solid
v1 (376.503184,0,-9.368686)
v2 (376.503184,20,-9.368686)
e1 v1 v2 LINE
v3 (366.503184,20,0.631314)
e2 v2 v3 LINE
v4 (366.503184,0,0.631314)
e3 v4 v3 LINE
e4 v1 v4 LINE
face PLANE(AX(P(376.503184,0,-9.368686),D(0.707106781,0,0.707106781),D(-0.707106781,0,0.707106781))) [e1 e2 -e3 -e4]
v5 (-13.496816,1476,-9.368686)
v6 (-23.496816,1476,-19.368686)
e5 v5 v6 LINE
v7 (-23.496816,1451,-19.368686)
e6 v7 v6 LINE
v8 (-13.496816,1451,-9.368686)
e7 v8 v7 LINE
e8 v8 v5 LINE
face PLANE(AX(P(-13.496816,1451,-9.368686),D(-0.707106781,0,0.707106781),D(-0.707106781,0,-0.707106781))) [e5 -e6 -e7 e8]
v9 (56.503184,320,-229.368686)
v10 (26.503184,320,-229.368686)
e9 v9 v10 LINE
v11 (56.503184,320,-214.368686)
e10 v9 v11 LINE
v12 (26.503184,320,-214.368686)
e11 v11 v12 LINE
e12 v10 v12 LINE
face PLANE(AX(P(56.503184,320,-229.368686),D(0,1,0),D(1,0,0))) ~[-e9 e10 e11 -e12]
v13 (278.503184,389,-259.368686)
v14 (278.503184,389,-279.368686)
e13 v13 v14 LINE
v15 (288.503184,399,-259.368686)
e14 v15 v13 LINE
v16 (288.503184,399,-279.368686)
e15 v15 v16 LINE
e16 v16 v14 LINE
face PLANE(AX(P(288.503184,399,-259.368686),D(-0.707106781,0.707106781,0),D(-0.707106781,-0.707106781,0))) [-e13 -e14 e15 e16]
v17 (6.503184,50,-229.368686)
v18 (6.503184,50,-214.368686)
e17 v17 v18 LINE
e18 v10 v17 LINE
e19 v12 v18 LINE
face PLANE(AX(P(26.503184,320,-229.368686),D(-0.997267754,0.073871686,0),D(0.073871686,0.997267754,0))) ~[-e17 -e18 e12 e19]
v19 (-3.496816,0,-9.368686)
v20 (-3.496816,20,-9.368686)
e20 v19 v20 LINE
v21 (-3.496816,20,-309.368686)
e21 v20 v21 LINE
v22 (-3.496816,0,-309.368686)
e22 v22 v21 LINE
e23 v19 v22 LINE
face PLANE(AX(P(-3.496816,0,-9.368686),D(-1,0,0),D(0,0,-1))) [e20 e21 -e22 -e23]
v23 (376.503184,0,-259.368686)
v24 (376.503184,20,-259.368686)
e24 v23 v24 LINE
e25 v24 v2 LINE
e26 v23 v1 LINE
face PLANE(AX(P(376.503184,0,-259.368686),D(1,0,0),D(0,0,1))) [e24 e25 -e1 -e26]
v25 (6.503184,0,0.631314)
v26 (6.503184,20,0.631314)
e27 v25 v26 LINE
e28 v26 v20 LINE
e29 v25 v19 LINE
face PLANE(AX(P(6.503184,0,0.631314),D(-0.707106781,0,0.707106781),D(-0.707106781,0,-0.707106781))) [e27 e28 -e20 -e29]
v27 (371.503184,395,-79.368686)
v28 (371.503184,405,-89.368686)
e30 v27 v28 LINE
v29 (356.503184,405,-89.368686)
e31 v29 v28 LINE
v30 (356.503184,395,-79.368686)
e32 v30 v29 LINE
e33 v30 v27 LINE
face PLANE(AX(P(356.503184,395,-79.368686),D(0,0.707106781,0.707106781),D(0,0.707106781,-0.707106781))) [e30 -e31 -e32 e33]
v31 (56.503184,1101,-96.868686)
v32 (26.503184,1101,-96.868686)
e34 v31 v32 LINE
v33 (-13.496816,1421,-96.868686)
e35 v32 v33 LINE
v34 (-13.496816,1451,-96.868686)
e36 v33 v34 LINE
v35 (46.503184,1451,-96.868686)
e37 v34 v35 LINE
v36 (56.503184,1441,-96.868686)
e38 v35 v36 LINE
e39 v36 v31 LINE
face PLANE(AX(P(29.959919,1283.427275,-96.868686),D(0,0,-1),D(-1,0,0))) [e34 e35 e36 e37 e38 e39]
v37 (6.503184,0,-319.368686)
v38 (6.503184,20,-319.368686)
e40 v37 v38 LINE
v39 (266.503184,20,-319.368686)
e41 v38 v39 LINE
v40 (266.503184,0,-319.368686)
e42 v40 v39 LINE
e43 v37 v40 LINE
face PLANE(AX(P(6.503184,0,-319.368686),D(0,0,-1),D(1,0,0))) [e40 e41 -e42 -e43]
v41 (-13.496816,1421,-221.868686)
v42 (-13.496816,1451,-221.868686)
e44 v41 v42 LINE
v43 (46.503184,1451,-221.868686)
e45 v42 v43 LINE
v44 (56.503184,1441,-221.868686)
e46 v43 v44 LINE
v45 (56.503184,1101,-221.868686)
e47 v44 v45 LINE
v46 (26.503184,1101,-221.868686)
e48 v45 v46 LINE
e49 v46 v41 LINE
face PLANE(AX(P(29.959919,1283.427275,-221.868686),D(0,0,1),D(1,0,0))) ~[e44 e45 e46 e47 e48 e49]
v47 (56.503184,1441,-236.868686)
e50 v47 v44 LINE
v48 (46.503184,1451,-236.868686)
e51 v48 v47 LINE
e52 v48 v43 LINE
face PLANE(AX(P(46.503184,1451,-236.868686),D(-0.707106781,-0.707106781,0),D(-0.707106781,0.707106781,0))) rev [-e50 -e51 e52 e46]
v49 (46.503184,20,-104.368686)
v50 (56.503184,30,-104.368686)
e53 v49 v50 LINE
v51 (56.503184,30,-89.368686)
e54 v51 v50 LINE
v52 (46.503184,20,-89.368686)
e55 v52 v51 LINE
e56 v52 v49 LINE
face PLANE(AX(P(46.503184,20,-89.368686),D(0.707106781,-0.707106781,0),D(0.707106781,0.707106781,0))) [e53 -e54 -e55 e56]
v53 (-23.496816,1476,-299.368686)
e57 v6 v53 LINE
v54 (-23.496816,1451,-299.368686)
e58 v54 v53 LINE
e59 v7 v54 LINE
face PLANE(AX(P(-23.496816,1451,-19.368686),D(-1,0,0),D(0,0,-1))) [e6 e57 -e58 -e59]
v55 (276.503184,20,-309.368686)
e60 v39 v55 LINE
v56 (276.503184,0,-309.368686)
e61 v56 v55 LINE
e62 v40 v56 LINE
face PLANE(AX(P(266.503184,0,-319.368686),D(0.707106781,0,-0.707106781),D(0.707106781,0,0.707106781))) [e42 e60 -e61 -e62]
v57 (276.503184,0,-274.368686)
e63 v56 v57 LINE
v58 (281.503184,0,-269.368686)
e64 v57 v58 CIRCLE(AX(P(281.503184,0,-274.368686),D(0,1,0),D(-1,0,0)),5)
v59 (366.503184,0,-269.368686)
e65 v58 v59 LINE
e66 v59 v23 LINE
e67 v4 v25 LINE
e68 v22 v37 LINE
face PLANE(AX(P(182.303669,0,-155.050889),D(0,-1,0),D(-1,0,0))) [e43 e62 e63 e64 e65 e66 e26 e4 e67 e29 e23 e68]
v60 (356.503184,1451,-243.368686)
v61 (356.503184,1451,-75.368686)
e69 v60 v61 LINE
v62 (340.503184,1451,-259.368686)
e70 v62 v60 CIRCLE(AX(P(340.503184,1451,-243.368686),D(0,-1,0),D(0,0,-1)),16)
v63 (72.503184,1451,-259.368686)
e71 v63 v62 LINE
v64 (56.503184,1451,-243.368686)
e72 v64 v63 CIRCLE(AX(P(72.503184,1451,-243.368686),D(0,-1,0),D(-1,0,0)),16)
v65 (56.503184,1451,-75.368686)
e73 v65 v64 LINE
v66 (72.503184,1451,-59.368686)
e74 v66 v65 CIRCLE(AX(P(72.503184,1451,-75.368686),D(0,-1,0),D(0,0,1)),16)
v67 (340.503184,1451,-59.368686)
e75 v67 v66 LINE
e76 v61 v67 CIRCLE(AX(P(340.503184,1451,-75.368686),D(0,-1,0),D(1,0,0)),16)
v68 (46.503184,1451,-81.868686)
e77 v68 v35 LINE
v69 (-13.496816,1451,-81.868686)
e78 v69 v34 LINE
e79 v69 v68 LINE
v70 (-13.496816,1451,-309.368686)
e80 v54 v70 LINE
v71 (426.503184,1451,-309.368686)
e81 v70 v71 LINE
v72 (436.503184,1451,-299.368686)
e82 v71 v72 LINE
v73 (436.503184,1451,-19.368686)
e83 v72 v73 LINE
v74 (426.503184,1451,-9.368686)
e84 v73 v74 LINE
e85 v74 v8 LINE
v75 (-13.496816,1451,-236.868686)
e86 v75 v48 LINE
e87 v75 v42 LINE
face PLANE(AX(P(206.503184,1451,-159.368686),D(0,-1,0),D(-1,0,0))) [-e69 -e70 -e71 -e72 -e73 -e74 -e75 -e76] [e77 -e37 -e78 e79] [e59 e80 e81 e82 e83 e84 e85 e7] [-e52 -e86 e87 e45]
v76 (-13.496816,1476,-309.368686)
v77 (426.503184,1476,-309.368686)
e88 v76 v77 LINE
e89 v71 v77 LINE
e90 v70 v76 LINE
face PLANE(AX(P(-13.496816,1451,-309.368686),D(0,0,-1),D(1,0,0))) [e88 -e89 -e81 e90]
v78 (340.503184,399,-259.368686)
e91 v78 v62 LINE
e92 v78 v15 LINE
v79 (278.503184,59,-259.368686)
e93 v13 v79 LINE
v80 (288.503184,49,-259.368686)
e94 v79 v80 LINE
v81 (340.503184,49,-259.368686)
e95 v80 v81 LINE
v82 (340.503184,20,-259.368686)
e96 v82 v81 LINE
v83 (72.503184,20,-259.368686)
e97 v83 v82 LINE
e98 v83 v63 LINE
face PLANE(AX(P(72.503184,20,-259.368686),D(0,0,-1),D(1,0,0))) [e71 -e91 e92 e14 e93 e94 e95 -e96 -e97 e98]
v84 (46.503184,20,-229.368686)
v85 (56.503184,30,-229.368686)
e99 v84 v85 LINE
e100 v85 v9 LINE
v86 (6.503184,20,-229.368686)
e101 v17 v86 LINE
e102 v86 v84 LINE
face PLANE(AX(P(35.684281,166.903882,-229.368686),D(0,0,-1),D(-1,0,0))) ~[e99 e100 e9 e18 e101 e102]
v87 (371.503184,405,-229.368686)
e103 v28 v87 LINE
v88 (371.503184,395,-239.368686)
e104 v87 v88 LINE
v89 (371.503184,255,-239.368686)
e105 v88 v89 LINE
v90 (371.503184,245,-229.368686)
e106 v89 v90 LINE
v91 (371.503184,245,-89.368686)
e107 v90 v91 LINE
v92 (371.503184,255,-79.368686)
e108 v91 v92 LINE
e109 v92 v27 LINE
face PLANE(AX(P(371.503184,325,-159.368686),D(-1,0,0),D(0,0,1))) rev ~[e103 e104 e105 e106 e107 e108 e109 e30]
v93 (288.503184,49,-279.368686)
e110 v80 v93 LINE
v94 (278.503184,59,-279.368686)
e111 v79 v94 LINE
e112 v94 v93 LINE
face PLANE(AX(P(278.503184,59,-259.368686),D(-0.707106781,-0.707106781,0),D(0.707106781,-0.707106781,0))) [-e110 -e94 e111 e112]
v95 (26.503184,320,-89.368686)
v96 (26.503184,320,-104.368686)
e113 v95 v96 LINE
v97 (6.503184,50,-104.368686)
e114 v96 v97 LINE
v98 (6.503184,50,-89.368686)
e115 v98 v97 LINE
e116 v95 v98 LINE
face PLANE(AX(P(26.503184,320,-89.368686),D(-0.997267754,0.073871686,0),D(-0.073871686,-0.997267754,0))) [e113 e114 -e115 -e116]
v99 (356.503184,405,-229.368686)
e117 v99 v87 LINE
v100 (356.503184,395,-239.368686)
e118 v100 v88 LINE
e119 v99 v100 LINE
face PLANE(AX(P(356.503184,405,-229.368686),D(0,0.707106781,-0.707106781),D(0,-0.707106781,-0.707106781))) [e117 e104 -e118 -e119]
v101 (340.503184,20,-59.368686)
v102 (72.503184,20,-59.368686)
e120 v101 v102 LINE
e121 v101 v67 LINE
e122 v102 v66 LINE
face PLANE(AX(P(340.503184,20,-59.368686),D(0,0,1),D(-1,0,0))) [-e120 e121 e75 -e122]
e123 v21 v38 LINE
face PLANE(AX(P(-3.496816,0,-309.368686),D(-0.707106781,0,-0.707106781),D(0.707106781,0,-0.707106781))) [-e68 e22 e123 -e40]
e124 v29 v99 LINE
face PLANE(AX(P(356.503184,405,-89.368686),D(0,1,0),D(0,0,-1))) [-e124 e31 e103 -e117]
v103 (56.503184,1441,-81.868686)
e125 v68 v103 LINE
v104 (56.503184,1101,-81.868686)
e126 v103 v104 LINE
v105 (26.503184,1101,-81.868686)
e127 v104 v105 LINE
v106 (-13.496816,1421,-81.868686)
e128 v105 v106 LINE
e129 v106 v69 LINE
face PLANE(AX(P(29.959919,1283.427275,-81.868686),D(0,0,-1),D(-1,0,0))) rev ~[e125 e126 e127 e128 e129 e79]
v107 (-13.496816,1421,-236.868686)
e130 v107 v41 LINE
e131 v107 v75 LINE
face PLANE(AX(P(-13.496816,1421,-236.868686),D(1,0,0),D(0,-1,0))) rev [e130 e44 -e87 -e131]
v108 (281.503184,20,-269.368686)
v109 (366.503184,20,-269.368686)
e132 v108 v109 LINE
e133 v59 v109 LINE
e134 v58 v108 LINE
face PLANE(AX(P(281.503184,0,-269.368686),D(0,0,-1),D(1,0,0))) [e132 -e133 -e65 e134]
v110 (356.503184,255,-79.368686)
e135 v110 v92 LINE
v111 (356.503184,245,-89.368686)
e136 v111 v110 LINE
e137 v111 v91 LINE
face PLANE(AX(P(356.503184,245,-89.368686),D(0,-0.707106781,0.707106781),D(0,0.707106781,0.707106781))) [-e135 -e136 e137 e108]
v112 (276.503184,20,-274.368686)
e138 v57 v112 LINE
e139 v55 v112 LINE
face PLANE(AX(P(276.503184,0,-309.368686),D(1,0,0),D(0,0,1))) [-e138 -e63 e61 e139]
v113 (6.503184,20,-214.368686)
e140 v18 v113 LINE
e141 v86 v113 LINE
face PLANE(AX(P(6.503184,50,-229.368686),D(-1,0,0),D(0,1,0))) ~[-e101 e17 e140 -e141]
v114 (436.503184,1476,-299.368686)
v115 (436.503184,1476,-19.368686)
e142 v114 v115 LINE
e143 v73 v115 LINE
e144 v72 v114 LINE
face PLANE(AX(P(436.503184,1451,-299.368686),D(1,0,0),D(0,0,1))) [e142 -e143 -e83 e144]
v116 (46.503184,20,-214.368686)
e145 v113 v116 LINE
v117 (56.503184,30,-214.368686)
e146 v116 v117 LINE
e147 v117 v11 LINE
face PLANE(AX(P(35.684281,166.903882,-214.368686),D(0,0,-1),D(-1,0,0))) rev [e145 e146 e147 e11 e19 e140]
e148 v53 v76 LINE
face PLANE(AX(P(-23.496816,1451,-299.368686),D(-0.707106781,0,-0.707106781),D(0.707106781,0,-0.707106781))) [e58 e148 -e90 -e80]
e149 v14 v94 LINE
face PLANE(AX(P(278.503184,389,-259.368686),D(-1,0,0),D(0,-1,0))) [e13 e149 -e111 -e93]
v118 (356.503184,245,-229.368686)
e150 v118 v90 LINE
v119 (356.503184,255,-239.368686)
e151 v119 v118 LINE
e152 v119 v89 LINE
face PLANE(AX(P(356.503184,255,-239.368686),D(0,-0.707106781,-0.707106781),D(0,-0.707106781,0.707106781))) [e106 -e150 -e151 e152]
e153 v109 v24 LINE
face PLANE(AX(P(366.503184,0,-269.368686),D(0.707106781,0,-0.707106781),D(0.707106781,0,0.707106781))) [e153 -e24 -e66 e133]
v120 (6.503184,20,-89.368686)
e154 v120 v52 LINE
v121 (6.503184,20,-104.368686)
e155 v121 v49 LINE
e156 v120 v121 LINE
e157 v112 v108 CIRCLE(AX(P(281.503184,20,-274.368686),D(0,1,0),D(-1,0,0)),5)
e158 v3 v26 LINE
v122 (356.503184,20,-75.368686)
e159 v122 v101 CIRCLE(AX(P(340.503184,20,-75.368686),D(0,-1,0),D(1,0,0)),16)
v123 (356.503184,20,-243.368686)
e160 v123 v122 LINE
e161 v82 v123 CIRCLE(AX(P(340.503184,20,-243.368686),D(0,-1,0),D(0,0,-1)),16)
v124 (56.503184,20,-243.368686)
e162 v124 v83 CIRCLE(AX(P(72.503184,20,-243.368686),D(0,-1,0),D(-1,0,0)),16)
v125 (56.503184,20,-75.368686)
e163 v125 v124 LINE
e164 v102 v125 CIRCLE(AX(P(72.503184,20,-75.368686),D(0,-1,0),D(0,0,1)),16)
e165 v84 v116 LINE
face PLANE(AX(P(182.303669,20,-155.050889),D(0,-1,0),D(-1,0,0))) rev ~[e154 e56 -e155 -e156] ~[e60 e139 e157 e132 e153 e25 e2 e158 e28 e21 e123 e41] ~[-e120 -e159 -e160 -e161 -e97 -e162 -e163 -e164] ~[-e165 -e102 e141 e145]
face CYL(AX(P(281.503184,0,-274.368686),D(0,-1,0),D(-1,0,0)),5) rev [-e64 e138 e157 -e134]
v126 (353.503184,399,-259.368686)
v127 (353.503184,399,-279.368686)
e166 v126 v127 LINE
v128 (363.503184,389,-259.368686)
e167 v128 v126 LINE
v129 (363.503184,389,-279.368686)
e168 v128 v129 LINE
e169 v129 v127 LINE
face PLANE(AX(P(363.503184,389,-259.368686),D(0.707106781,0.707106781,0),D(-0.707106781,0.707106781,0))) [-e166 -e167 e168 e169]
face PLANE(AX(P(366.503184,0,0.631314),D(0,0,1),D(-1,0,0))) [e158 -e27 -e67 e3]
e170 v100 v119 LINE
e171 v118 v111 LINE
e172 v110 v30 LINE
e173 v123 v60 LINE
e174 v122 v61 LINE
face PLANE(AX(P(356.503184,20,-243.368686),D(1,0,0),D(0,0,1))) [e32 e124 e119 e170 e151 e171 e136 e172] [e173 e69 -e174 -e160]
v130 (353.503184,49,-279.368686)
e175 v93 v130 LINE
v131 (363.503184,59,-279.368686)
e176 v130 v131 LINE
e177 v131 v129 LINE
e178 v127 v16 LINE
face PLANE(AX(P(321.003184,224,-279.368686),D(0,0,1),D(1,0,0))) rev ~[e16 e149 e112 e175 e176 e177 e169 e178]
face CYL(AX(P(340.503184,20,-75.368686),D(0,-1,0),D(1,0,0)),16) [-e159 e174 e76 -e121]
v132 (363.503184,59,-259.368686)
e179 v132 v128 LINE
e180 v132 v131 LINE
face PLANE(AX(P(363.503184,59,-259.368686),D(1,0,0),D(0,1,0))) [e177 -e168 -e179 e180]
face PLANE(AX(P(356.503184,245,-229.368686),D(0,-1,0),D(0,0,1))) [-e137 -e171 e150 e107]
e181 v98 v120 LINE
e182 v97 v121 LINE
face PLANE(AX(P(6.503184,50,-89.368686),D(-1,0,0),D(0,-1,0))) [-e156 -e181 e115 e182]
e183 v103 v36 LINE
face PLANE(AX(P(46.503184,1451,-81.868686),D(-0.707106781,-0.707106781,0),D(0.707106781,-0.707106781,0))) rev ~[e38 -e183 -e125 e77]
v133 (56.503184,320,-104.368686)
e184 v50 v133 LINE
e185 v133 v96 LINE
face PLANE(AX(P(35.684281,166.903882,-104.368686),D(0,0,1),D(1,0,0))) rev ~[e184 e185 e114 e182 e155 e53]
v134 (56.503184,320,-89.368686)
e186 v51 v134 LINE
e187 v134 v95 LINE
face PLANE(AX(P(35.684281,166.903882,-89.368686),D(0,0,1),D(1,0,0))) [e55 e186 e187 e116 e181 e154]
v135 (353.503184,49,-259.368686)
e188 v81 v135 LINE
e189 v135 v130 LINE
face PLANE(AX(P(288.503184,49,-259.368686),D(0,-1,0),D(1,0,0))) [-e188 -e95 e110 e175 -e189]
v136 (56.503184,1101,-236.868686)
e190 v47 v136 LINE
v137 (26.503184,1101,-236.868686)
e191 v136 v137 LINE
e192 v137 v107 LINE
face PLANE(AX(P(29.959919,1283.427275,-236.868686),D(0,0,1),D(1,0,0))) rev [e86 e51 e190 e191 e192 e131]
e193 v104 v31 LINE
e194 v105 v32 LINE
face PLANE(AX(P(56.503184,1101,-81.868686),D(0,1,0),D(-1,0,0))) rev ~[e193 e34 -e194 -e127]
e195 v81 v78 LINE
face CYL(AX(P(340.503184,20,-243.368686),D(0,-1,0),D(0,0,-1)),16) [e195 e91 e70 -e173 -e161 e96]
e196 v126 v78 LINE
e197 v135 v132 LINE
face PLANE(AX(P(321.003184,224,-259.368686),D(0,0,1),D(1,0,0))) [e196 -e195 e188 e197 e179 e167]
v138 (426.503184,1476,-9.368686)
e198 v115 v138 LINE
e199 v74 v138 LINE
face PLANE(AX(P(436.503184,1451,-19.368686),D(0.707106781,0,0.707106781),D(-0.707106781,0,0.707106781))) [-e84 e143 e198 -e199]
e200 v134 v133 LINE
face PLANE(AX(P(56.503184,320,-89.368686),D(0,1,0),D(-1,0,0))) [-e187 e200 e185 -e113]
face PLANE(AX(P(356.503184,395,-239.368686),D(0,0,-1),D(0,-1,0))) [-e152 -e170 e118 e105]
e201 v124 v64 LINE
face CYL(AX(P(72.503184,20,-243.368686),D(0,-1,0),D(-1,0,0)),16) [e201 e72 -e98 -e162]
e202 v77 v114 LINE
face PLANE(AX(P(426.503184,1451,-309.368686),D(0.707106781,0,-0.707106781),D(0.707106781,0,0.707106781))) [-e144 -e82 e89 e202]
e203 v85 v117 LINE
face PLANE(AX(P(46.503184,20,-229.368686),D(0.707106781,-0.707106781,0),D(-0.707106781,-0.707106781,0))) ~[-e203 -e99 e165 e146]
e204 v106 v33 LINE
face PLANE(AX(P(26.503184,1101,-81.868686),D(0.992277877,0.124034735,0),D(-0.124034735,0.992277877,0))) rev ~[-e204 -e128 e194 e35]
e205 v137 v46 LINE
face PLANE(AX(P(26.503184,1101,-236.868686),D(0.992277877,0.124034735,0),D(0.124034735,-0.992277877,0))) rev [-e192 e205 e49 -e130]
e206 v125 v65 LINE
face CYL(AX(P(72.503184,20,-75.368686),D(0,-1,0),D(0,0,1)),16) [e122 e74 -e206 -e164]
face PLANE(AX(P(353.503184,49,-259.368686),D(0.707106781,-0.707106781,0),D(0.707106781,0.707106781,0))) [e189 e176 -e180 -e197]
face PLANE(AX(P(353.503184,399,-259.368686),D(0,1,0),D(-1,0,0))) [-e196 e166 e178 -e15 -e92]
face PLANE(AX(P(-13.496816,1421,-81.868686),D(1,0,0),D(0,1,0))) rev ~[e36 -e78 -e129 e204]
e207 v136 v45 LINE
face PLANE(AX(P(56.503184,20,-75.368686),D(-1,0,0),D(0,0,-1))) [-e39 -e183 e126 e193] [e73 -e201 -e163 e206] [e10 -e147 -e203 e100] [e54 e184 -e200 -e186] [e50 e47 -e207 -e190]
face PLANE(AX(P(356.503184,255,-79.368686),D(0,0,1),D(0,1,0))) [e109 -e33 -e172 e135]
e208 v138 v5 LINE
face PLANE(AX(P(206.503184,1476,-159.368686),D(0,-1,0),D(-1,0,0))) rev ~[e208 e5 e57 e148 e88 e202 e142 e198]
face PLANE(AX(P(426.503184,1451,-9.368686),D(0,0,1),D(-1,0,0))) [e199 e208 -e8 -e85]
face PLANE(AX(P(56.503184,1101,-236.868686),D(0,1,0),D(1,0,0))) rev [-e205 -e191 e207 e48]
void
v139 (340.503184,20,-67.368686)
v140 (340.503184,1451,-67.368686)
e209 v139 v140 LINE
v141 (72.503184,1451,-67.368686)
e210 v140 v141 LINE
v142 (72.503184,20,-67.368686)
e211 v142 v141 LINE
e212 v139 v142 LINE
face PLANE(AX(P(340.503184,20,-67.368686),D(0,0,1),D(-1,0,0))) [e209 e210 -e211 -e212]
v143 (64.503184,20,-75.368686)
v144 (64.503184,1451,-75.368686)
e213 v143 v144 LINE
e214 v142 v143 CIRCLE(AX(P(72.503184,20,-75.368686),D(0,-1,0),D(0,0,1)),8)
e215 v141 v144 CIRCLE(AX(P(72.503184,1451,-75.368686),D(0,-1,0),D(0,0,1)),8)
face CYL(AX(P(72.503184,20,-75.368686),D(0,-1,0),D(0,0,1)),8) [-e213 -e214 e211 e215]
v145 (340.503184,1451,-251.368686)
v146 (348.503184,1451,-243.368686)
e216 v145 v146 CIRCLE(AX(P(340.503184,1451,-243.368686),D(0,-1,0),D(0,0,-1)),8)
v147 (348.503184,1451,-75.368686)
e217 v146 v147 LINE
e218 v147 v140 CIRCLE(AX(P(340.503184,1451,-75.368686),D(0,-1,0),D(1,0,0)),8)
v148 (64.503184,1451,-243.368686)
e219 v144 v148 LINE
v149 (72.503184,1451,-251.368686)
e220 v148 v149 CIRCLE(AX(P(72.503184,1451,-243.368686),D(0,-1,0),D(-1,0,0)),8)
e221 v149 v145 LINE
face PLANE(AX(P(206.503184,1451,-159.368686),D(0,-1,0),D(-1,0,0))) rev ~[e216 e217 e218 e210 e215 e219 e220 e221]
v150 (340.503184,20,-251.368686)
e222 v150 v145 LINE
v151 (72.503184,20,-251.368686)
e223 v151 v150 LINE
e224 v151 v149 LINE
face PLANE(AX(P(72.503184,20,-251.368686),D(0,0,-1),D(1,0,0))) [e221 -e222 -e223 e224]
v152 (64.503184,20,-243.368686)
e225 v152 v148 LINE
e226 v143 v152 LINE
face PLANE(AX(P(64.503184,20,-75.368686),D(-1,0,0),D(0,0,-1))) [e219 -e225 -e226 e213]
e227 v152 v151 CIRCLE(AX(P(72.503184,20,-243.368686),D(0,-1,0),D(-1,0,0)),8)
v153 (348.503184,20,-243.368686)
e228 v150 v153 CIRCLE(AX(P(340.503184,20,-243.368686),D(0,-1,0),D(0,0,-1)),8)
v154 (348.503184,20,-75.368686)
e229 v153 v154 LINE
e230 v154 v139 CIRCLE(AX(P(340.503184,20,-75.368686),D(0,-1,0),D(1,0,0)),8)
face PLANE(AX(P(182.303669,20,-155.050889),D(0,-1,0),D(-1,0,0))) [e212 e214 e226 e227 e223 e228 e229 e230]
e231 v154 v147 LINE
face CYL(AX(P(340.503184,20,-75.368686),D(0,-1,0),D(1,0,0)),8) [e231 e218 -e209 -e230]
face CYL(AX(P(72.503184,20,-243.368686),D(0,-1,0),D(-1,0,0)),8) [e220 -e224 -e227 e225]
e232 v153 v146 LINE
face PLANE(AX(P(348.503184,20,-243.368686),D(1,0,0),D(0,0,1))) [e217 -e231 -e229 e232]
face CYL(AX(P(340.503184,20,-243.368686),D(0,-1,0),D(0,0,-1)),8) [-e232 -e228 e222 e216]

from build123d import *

# Parameters (mm, degrees)
BOSS_EXTRUDE1_DEPTH  = 20
BOSS_EXTRUDE2_DEPTH  = 1431
BOSS_EXTRUDE3_DEPTH  = 25
BOSS_EXTRUDE4_START  = -22.5
BOSS_EXTRUDE4_DEPTH  = 15
BOSS_EXTRUDE5_DEPTH  = 15
BOSS_EXTRUDE9_START  = -30
BOSS_EXTRUDE9_DEPTH  = 15
BOSS_EXTRUDE10_DEPTH = 20


with BuildPart() as part:
    # Sketch1 → Boss-Extrude1 (new body)
    with BuildSketch(Plane(origin=(0, 0, 0), x_dir=(1, 0, 0), z_dir=(0, 1, 0))):
        with BuildLine():
            Line((-3.496816057, 9.368686005), (-3.496816057, 309.368686005))
            Line((-3.496816057, 309.368686005), (6.503183943, 319.368686005))
            Line((6.503183943, 319.368686005), (141.657748152, 319.368686005))
            Line((141.657748152, 319.368686005), (266.503183943, 319.368686005))
            Line((266.503183943, 319.368686005), (276.503183943, 309.368686005))
            Line((276.503183943, 309.368686005), (276.503183943, 274.368686005))
            ThreePointArc((276.503183943, 274.368686005), (277.967650037, 270.833152099), (281.503183943, 269.368686005))
            Line((281.503183943, 269.368686005), (366.503183943, 269.368686005))
            Line((366.503183943, 269.368686005), (376.503183943, 259.368686005))
            Line((376.503183943, 259.368686005), (376.503183943, 9.368686005))
            Line((376.503183943, 9.368686005), (366.503183943, -0.631313995))
            Line((366.503183943, -0.631313995), (6.503183943, -0.631313995))
            Line((6.503183943, -0.631313995), (-3.496816057, 9.368686005))
        make_face()
    extrude(amount=BOSS_EXTRUDE1_DEPTH)

    # Sketch2 → Boss-Extrude2 (add)
    with BuildSketch(Plane(origin=(0, 20, 0), x_dir=(1, 0, 0), z_dir=(0, 1, 0))):
        with BuildLine():
            Line((72.503183943, 259.368686005), (340.503183943, 259.368686005))
            ThreePointArc((340.503183943, 259.368686005), (351.816892442, 254.682394504), (356.503183943, 243.368686005))
            Line((356.503183943, 243.368686005), (356.503183943, 75.368686005))
            ThreePointArc((356.503183943, 75.368686005), (351.816892442, 64.054977506), (340.503183943, 59.368686005))
            Line((340.503183943, 59.368686005), (72.503183943, 59.368686005))
            ThreePointArc((72.503183943, 59.368686005), (61.189475444, 64.054977506), (56.503183943, 75.368686005))
            Line((56.503183943, 75.368686005), (56.503183943, 243.368686005))
            ThreePointArc((56.503183943, 243.368686005), (61.189475444, 254.682394504), (72.503183943, 259.368686005))
        make_face()
        with BuildLine():
            Line((72.503183943, 251.368686005), (340.503183943, 251.368686005))
            ThreePointArc((340.503183943, 251.368686005), (346.160038192, 249.025540255), (348.503183943, 243.368686005))
            Line((348.503183943, 243.368686005), (348.503183943, 75.368686005))
            ThreePointArc((348.503183943, 75.368686005), (346.160038192, 69.711831756), (340.503183943, 67.368686005))
            Line((340.503183943, 67.368686005), (72.503183943, 67.368686005))
            ThreePointArc((72.503183943, 67.368686005), (66.846329693, 69.711831756), (64.503183943, 75.368686005))
            Line((64.503183943, 75.368686005), (64.503183943, 243.368686005))
            ThreePointArc((64.503183943, 243.368686005), (66.846329693, 249.025540255), (72.503183943, 251.368686005))
        make_face(mode=Mode.SUBTRACT)
    extrude(amount=BOSS_EXTRUDE2_DEPTH)

    # Sketch3 → Boss-Extrude3 (add)
    with BuildSketch(Plane(origin=(0, 1451, 0), x_dir=(1, 0, 0), z_dir=(0, 1, 0))):
        Polygon((-13.496816057, 309.368686005), (426.503183943, 309.368686005), (436.503183943, 299.368686005), (436.503183943, 19.368686005), (426.503183943, 9.368686005), (-13.496816057, 9.368686005), (-23.496816057, 19.368686005), (-23.496816057, 299.368686005), align=None)
    extrude(amount=BOSS_EXTRUDE3_DEPTH)

    # Sketch4 → Boss-Extrude4 (add)
    with BuildSketch(Plane.XY.offset(-59.368686005).offset(BOSS_EXTRUDE4_START)):
        Polygon((-13.496816057, 1451), (46.503183943, 1451), (56.503183943, 1441), (56.503183943, 1101), (26.503183943, 1101), (-13.496816057, 1421), align=None)
    boss_extrude4 = extrude(amount=-BOSS_EXTRUDE4_DEPTH)

    # Mirror1: Boss-Extrude4 across plane
    add(boss_extrude4.mirror(Plane.XY.offset(-159.368686005)))

    # Sketch5 → Boss-Extrude5 (add)
    with BuildSketch(Plane(origin=(356.503183943, 0, 0), x_dir=(0, 0, -1), z_dir=(1, 0, 0))):
        Polygon((89.368686005, 405), (229.368686005, 405), (239.368686005, 395), (239.368686005, 255), (229.368686005, 245), (89.368686005, 245), (79.368686005, 255), (79.368686005, 395), align=None)
    extrude(amount=BOSS_EXTRUDE5_DEPTH)

    # Sketch9 → Boss-Extrude9 (add)
    with BuildSketch(Plane.XY.offset(-59.368686005).offset(BOSS_EXTRUDE9_START)):
        Polygon((56.503183943, 30), (56.503183943, 320), (26.503183943, 320), (6.503183943, 50), (6.503183943, 20), (46.503183943, 20), align=None)
    boss_extrude9 = extrude(amount=-BOSS_EXTRUDE9_DEPTH)

    # Mirror2: Boss-Extrude9 across plane
    add(boss_extrude9.mirror(Plane.XY.offset(-159.368686005)))

    # Sketch10 → Boss-Extrude10 (add)
    with BuildSketch(Plane(origin=(0, 0, -259.368686005), x_dir=(-1, 0, 0), z_dir=(0, 0, -1))):
        Polygon((-353.503183943, 399), (-288.503183943, 399), (-278.503183943, 389), (-278.503183943, 59), (-288.503183943, 49), (-353.503183943, 49), (-363.503183943, 59), (-363.503183943, 389), align=None)
    extrude(amount=BOSS_EXTRUDE10_DEPTH)


solid = part.part
